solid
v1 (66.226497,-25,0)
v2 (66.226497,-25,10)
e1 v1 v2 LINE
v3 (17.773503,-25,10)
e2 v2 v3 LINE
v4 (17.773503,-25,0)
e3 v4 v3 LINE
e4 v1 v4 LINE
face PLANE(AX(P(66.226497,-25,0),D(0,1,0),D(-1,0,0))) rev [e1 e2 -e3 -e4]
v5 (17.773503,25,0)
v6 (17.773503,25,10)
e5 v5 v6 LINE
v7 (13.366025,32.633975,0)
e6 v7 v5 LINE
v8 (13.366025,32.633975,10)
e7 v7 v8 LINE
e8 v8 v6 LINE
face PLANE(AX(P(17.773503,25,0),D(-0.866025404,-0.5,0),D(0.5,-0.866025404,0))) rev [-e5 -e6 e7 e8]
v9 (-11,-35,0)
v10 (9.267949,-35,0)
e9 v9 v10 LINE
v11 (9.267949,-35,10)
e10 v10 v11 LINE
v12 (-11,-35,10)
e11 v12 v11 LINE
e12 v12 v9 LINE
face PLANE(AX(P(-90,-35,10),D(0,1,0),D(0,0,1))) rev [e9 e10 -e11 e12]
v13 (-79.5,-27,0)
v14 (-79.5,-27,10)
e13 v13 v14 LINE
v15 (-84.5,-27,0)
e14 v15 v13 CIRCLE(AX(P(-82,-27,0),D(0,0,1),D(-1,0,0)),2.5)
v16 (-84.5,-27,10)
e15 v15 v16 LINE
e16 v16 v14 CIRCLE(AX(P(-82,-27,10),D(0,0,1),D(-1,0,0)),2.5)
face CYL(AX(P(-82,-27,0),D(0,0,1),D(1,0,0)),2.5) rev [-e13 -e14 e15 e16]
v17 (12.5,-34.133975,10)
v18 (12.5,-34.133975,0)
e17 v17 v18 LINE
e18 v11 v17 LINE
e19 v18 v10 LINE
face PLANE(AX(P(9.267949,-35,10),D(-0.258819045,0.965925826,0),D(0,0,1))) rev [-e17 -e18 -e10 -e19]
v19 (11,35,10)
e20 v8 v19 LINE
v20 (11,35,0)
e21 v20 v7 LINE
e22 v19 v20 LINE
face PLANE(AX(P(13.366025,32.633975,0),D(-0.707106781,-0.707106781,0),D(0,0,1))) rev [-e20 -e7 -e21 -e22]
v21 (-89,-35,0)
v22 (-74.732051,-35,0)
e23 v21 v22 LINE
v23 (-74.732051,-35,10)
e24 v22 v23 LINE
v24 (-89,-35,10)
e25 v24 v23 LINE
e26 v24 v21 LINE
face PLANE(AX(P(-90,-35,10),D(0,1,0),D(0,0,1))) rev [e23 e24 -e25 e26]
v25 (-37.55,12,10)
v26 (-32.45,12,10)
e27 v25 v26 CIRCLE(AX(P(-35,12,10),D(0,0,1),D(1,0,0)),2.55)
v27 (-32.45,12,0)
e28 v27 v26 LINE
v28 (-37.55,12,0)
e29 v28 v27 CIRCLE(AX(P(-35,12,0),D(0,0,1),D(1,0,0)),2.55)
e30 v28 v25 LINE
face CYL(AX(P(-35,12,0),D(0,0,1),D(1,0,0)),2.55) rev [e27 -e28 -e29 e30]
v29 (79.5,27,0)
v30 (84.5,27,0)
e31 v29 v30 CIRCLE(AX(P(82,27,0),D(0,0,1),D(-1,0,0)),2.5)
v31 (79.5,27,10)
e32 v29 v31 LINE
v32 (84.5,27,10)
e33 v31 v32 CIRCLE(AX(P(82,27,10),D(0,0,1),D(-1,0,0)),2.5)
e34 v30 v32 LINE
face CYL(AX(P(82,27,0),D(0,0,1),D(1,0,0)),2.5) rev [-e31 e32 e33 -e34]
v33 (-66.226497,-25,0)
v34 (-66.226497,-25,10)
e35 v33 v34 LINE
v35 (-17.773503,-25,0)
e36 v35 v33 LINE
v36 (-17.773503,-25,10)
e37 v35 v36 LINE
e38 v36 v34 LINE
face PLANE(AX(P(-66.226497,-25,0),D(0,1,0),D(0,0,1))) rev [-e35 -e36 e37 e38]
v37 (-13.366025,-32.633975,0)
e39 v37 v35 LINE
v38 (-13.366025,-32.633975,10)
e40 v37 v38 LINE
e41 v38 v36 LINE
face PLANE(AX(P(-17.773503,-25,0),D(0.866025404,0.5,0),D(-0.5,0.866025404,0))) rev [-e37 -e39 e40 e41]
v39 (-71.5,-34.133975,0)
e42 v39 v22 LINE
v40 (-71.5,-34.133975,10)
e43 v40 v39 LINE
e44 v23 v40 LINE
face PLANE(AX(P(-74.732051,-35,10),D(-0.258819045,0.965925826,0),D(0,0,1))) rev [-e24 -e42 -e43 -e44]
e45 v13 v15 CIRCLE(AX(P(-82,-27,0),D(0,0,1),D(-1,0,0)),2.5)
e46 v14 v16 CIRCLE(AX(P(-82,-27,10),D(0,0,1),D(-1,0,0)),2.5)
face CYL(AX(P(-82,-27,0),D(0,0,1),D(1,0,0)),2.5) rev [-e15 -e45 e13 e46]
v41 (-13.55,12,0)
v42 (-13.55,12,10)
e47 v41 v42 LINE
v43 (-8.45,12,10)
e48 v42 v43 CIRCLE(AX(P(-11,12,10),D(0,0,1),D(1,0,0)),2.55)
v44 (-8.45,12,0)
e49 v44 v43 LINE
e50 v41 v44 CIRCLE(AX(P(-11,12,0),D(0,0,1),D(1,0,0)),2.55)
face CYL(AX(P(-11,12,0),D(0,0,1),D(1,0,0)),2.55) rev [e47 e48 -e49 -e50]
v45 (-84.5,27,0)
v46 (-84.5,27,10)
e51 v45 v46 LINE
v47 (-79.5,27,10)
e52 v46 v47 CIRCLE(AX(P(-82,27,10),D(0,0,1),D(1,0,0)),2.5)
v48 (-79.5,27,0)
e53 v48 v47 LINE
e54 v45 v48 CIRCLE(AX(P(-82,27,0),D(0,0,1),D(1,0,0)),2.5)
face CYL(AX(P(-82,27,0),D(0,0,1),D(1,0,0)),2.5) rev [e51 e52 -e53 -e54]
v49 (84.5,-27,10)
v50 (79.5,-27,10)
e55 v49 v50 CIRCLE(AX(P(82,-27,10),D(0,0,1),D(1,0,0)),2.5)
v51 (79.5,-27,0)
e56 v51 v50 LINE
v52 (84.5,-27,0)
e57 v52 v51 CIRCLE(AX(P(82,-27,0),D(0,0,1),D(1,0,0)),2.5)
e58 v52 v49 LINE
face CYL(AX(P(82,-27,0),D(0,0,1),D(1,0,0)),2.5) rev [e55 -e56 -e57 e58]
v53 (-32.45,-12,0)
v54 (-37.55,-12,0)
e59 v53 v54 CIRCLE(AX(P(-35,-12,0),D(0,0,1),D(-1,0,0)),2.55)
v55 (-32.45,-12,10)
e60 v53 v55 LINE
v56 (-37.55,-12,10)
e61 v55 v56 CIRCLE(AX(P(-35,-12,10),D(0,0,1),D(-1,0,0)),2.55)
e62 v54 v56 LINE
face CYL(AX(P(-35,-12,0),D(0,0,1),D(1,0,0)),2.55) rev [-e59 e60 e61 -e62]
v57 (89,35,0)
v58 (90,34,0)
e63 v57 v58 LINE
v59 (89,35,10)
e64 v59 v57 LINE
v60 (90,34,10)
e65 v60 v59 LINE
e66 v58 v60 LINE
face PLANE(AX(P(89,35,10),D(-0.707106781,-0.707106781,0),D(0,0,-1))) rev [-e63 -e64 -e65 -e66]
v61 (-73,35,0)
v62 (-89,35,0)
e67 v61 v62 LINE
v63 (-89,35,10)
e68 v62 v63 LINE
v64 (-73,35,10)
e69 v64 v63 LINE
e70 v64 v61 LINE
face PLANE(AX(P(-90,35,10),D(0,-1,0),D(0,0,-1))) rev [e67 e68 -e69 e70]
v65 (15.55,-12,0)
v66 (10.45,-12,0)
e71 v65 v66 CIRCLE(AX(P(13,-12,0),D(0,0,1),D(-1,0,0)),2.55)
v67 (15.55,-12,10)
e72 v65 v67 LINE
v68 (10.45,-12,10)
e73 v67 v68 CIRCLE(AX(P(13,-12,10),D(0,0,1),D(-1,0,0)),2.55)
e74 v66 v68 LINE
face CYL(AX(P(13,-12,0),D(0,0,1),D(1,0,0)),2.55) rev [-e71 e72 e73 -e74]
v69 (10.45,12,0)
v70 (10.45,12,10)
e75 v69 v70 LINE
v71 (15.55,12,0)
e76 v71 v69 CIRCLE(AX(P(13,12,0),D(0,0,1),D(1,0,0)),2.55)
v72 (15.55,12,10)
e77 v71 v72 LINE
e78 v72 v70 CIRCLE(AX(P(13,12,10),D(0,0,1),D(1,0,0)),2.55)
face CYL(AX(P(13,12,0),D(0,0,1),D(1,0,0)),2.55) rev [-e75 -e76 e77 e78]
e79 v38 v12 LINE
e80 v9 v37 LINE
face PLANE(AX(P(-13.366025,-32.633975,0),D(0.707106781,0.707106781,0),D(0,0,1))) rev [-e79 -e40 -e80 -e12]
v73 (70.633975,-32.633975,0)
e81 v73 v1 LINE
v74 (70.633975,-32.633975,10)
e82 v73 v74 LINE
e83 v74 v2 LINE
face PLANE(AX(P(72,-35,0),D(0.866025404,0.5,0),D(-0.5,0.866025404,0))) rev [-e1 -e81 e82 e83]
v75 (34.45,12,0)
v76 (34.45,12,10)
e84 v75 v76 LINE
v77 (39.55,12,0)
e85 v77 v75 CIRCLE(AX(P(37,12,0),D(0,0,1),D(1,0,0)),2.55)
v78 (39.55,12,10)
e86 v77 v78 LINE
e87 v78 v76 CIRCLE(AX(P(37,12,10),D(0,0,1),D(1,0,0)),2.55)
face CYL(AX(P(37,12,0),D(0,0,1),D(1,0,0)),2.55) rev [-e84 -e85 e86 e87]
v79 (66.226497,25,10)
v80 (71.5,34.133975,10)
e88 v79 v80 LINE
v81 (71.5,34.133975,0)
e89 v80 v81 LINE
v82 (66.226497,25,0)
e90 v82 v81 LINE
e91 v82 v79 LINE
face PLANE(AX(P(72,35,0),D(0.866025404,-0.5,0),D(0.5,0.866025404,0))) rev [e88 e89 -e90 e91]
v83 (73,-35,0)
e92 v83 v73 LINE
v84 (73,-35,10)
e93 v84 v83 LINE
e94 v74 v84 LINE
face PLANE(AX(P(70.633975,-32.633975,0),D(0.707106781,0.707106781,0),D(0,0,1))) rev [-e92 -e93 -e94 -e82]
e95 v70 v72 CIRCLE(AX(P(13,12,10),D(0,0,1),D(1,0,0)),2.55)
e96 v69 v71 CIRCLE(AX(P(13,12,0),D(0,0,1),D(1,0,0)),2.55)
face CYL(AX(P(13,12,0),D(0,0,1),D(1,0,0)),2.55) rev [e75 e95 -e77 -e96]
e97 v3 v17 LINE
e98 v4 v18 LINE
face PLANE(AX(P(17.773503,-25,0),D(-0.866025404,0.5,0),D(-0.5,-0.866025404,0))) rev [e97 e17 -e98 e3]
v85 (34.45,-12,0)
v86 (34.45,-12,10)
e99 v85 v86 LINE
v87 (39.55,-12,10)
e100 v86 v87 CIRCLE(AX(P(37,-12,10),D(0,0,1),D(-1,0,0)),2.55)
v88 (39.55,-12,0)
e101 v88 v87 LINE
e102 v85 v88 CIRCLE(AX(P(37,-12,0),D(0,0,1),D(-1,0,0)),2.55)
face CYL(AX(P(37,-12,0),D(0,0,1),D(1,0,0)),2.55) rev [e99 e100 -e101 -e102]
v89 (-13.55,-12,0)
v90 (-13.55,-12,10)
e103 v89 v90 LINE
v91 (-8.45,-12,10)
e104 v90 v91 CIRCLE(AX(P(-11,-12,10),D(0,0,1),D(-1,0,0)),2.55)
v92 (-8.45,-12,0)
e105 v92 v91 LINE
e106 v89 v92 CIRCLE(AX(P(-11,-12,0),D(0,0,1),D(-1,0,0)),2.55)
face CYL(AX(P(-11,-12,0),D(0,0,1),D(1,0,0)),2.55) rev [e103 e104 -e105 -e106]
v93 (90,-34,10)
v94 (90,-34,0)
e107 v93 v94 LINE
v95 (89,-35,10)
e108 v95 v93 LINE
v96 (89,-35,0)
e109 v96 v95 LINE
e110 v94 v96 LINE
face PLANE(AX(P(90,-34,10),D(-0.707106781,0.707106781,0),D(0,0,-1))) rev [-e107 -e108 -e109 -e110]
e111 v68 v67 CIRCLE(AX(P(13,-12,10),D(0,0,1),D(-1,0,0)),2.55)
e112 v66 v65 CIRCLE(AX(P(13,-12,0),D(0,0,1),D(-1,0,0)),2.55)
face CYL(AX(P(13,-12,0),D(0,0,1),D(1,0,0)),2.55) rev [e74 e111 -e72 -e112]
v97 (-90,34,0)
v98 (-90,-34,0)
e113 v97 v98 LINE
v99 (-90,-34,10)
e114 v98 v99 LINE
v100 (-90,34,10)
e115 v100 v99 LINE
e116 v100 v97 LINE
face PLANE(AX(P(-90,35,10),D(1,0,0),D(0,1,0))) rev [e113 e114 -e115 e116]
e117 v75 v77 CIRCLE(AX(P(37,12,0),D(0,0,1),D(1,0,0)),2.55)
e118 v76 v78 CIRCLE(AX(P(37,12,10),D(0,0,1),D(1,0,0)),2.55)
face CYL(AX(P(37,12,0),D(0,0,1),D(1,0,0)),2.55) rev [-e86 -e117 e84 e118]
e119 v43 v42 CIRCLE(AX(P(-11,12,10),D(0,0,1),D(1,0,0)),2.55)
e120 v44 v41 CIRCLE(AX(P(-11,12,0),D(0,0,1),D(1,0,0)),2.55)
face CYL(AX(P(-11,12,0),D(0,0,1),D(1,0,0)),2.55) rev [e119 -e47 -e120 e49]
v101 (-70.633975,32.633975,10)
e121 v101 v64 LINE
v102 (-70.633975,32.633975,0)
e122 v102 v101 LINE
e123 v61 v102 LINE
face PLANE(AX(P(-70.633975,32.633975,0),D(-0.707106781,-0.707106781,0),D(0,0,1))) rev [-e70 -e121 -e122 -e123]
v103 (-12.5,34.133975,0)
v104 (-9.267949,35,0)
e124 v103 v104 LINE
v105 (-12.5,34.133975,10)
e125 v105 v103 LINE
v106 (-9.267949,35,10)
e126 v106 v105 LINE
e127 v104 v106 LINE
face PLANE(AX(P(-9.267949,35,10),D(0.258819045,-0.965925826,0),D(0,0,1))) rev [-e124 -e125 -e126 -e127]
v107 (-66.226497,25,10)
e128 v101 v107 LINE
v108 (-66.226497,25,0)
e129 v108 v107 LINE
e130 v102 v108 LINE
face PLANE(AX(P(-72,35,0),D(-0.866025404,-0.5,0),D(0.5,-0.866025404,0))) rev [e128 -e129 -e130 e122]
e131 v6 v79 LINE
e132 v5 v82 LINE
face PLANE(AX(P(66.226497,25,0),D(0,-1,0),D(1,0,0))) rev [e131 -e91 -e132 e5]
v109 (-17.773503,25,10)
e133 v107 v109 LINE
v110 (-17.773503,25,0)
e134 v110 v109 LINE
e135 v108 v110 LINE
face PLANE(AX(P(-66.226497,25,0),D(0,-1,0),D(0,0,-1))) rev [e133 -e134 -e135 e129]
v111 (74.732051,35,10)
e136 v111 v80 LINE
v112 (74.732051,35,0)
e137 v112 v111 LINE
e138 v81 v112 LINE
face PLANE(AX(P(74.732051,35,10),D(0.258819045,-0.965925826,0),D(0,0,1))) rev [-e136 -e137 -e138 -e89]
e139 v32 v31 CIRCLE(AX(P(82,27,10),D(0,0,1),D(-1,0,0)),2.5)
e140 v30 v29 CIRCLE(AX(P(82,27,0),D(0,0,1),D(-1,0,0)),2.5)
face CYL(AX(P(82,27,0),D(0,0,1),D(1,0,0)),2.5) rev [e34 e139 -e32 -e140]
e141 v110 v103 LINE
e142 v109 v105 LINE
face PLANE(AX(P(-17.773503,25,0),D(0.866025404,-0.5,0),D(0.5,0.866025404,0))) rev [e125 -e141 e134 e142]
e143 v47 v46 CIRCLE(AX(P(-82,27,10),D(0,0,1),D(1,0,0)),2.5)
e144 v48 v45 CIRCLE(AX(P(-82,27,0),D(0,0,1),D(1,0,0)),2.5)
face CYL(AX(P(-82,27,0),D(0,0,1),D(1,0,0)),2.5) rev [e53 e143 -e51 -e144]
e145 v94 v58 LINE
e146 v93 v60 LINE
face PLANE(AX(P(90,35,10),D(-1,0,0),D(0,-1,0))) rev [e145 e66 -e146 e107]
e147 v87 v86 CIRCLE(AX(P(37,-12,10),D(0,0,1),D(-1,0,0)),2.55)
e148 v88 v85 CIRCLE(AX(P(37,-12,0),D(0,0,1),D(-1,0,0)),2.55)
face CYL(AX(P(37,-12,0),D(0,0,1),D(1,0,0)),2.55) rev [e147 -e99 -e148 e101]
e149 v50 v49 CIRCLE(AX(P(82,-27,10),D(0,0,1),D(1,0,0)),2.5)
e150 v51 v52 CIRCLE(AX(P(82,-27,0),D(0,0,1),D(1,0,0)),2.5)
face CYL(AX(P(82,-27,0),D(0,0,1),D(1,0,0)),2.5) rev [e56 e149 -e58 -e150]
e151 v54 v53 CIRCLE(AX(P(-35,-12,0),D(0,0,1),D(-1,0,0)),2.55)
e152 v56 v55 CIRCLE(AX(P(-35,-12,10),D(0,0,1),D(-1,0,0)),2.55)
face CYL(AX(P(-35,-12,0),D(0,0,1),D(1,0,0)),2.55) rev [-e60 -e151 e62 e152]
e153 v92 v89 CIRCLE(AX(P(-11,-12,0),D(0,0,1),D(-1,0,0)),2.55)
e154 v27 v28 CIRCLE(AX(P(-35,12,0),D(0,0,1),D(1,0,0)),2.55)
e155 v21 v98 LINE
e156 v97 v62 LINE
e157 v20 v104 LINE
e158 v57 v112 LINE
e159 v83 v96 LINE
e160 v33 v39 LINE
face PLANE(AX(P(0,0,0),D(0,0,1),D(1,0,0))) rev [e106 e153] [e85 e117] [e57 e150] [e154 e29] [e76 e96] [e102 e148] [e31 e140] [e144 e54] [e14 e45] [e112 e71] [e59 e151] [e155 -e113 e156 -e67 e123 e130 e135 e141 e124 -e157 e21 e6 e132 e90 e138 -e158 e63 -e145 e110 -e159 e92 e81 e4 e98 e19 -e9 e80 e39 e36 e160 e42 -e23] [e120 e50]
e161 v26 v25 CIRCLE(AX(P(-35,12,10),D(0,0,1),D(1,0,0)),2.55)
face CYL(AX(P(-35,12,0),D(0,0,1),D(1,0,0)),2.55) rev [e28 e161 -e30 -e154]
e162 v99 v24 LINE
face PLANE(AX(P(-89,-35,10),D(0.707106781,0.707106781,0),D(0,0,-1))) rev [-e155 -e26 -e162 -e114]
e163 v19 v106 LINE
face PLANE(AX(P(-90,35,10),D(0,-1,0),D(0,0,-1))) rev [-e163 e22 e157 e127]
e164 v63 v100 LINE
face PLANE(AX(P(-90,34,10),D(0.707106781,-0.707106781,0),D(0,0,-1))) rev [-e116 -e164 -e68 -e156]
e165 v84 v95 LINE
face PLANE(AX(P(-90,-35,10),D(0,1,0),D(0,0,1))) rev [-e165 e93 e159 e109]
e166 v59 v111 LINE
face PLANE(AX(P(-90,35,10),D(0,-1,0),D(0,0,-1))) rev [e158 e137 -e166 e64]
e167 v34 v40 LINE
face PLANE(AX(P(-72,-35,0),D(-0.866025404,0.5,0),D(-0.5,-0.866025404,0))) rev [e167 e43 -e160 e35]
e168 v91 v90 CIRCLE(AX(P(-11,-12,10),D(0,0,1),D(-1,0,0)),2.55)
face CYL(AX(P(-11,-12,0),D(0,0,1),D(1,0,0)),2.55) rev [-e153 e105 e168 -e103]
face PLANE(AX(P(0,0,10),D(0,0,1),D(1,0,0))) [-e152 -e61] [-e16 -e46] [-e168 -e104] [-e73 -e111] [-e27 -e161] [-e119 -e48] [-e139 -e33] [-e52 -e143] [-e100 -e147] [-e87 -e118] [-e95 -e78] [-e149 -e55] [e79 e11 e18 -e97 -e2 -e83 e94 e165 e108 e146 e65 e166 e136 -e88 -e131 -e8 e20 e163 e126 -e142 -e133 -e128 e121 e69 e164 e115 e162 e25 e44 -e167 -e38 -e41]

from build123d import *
from OCP.BRepFilletAPI import BRepFilletAPI_MakeChamfer

# Parameters (mm, degrees)
SKETCH1_W           = 180
SKETCH1_H           = 70
BOSS_EXTRUDE1_DEPTH = 10
CUT_EXTRUDE1_DEPTH  = 98.082439195
SKETCH3_R           = 2.5
CUT_EXTRUDE2_DEPTH  = 98.082439195
CHAMFER1_SIZE       = 1
CHAMFER1_SIZE2      = 2.732050808
SKETCH4_R           = 2.55
CUT_EXTRUDE3_DEPTH  = 98.082439195


with BuildPart() as part:
    # Sketch1 → Boss-Extrude1 (new body)
    with BuildSketch(Plane.XY):
        Rectangle(SKETCH1_W, SKETCH1_H)
    extrude(amount=BOSS_EXTRUDE1_DEPTH)

    # Sketch2 → Cut-Extrude1 (cut, through all)
    with BuildSketch(Plane.XY.offset(10)):
        Polygon((-72, 35), (-66.226497308, 25), (-17.773502692, 25), (-12, 35), align=None)
        Polygon((72, 35), (12, 35), (17.773502692, 25), (66.226497308, 25), align=None)
        Polygon((72, -35), (66.226497308, -25), (17.773502692, -25), (12, -35), align=None)
        Polygon((-72, -35), (-12, -35), (-17.773502692, -25), (-66.226497308, -25), align=None)
    extrude(amount=-CUT_EXTRUDE1_DEPTH, mode=Mode.SUBTRACT)

    # Sketch3 → Cut-Extrude2 (cut, through all)
    with BuildSketch(Plane.XY.offset(10)):
        with Locations((-82, 27)):
            Circle(SKETCH3_R)
        with Locations(Location((82, 27, 0), (0, 0, 180))):
            Circle(SKETCH3_R)
        with Locations((82, -27)):
            Circle(SKETCH3_R)
        with Locations(Location((-82, -27, 0), (0, 0, 180))):
            Circle(SKETCH3_R)
    extrude(amount=-CUT_EXTRUDE2_DEPTH, mode=Mode.SUBTRACT)

    # Chamfer1: one chamfer whose edges measure the first distance from different faces: ONE call of the kernel's chamfer builder (chamfer() names one face for all edges)
    chamfer1_edges_1 = [part.edges().sort_by_distance(p)[0] for p in [
        (-72, -35, 5),
    ]]
    chamfer1_side_1 = [part.faces().sort_by_distance(p)[0] for p in [
        (-69.113248654, -30, 5),
    ]]
    chamfer1_edges_2 = [part.edges().sort_by_distance(p)[0] for p in [
        (-12, -35, 5),
    ]]
    chamfer1_side_2 = [part.faces().sort_by_distance(p)[0] for p in [
        (0, -35, 5),
    ]]
    chamfer1_edges_3 = [part.edges().sort_by_distance(p)[0] for p in [
        (72, -35, 5),
    ]]
    chamfer1_side_3 = [part.faces().sort_by_distance(p)[0] for p in [
        (81, -35, 5),
    ]]
    chamfer1_edges_4 = [part.edges().sort_by_distance(p)[0] for p in [
        (12, -35, 5),
    ]]
    chamfer1_side_4 = [part.faces().sort_by_distance(p)[0] for p in [
        (14.886751346, -30, 5),
    ]]
    chamfer1_edges_5 = [part.edges().sort_by_distance(p)[0] for p in [
        (72, 35, 5),
    ]]
    chamfer1_side_5 = [part.faces().sort_by_distance(p)[0] for p in [
        (69.113248654, 30, 5),
    ]]
    chamfer1_edges_6 = [part.edges().sort_by_distance(p)[0] for p in [
        (12, 35, 5),
    ]]
    chamfer1_side_6 = [part.faces().sort_by_distance(p)[0] for p in [
        (0, 35, 5),
    ]]
    chamfer1_edges_7 = [part.edges().sort_by_distance(p)[0] for p in [
        (-72, 35, 5),
    ]]
    chamfer1_side_7 = [part.faces().sort_by_distance(p)[0] for p in [
        (-81, 35, 5),
    ]]
    chamfer1_edges_8 = [part.edges().sort_by_distance(p)[0] for p in [
        (-12, 35, 5),
    ]]
    chamfer1_side_8 = [part.faces().sort_by_distance(p)[0] for p in [
        (-14.886751346, 30, 5),
    ]]
    chamfer1_edges_9 = [part.edges().sort_by_distance(p)[0] for p in [
        (90, -35, 5),
        (-90, -35, 5),
        (-90, 35, 5),
        (90, 35, 5),
    ]]
    chamfer1 = BRepFilletAPI_MakeChamfer(part.part.solid().wrapped)
    for e in chamfer1_edges_1:
        chamfer1.Add(CHAMFER1_SIZE, CHAMFER1_SIZE2, e.wrapped, chamfer1_side_1[0].wrapped)  # the first distance lies on this face
    for e in chamfer1_edges_2:
        chamfer1.Add(CHAMFER1_SIZE, CHAMFER1_SIZE2, e.wrapped, chamfer1_side_2[0].wrapped)  # the first distance lies on this face
    for e in chamfer1_edges_3:
        chamfer1.Add(CHAMFER1_SIZE, CHAMFER1_SIZE2, e.wrapped, chamfer1_side_3[0].wrapped)  # the first distance lies on this face
    for e in chamfer1_edges_4:
        chamfer1.Add(CHAMFER1_SIZE, CHAMFER1_SIZE2, e.wrapped, chamfer1_side_4[0].wrapped)  # the first distance lies on this face
    for e in chamfer1_edges_5:
        chamfer1.Add(CHAMFER1_SIZE, CHAMFER1_SIZE2, e.wrapped, chamfer1_side_5[0].wrapped)  # the first distance lies on this face
    for e in chamfer1_edges_6:
        chamfer1.Add(CHAMFER1_SIZE, CHAMFER1_SIZE2, e.wrapped, chamfer1_side_6[0].wrapped)  # the first distance lies on this face
    for e in chamfer1_edges_7:
        chamfer1.Add(CHAMFER1_SIZE, CHAMFER1_SIZE2, e.wrapped, chamfer1_side_7[0].wrapped)  # the first distance lies on this face
    for e in chamfer1_edges_8:
        chamfer1.Add(CHAMFER1_SIZE, CHAMFER1_SIZE2, e.wrapped, chamfer1_side_8[0].wrapped)  # the first distance lies on this face
    for e in chamfer1_edges_9:
        chamfer1.Add(CHAMFER1_SIZE, e.wrapped)
    add(Compound.cast(chamfer1.Shape()), mode=Mode.REPLACE)

    # Sketch4 → Cut-Extrude3 (cut, through all)
    with BuildSketch(Plane.XY.offset(10)):
        with Locations((-35, 12)):
            Circle(SKETCH4_R)
        with Locations((-11, 12)):
            Circle(SKETCH4_R)
        with Locations((13, 12)):
            Circle(SKETCH4_R)
        with Locations((37, 12)):
            Circle(SKETCH4_R)
        with Locations(Location((37, -12, 0), (0, 0, 180))):
            Circle(SKETCH4_R)
        with Locations(Location((13, -12, 0), (0, 0, 180))):
            Circle(SKETCH4_R)
        with Locations(Location((-11, -12, 0), (0, 0, 180))):
            Circle(SKETCH4_R)
        with Locations(Location((-35, -12, 0), (0, 0, 180))):
            Circle(SKETCH4_R)
    extrude(amount=-CUT_EXTRUDE3_DEPTH, mode=Mode.SUBTRACT)


solid = part.part
